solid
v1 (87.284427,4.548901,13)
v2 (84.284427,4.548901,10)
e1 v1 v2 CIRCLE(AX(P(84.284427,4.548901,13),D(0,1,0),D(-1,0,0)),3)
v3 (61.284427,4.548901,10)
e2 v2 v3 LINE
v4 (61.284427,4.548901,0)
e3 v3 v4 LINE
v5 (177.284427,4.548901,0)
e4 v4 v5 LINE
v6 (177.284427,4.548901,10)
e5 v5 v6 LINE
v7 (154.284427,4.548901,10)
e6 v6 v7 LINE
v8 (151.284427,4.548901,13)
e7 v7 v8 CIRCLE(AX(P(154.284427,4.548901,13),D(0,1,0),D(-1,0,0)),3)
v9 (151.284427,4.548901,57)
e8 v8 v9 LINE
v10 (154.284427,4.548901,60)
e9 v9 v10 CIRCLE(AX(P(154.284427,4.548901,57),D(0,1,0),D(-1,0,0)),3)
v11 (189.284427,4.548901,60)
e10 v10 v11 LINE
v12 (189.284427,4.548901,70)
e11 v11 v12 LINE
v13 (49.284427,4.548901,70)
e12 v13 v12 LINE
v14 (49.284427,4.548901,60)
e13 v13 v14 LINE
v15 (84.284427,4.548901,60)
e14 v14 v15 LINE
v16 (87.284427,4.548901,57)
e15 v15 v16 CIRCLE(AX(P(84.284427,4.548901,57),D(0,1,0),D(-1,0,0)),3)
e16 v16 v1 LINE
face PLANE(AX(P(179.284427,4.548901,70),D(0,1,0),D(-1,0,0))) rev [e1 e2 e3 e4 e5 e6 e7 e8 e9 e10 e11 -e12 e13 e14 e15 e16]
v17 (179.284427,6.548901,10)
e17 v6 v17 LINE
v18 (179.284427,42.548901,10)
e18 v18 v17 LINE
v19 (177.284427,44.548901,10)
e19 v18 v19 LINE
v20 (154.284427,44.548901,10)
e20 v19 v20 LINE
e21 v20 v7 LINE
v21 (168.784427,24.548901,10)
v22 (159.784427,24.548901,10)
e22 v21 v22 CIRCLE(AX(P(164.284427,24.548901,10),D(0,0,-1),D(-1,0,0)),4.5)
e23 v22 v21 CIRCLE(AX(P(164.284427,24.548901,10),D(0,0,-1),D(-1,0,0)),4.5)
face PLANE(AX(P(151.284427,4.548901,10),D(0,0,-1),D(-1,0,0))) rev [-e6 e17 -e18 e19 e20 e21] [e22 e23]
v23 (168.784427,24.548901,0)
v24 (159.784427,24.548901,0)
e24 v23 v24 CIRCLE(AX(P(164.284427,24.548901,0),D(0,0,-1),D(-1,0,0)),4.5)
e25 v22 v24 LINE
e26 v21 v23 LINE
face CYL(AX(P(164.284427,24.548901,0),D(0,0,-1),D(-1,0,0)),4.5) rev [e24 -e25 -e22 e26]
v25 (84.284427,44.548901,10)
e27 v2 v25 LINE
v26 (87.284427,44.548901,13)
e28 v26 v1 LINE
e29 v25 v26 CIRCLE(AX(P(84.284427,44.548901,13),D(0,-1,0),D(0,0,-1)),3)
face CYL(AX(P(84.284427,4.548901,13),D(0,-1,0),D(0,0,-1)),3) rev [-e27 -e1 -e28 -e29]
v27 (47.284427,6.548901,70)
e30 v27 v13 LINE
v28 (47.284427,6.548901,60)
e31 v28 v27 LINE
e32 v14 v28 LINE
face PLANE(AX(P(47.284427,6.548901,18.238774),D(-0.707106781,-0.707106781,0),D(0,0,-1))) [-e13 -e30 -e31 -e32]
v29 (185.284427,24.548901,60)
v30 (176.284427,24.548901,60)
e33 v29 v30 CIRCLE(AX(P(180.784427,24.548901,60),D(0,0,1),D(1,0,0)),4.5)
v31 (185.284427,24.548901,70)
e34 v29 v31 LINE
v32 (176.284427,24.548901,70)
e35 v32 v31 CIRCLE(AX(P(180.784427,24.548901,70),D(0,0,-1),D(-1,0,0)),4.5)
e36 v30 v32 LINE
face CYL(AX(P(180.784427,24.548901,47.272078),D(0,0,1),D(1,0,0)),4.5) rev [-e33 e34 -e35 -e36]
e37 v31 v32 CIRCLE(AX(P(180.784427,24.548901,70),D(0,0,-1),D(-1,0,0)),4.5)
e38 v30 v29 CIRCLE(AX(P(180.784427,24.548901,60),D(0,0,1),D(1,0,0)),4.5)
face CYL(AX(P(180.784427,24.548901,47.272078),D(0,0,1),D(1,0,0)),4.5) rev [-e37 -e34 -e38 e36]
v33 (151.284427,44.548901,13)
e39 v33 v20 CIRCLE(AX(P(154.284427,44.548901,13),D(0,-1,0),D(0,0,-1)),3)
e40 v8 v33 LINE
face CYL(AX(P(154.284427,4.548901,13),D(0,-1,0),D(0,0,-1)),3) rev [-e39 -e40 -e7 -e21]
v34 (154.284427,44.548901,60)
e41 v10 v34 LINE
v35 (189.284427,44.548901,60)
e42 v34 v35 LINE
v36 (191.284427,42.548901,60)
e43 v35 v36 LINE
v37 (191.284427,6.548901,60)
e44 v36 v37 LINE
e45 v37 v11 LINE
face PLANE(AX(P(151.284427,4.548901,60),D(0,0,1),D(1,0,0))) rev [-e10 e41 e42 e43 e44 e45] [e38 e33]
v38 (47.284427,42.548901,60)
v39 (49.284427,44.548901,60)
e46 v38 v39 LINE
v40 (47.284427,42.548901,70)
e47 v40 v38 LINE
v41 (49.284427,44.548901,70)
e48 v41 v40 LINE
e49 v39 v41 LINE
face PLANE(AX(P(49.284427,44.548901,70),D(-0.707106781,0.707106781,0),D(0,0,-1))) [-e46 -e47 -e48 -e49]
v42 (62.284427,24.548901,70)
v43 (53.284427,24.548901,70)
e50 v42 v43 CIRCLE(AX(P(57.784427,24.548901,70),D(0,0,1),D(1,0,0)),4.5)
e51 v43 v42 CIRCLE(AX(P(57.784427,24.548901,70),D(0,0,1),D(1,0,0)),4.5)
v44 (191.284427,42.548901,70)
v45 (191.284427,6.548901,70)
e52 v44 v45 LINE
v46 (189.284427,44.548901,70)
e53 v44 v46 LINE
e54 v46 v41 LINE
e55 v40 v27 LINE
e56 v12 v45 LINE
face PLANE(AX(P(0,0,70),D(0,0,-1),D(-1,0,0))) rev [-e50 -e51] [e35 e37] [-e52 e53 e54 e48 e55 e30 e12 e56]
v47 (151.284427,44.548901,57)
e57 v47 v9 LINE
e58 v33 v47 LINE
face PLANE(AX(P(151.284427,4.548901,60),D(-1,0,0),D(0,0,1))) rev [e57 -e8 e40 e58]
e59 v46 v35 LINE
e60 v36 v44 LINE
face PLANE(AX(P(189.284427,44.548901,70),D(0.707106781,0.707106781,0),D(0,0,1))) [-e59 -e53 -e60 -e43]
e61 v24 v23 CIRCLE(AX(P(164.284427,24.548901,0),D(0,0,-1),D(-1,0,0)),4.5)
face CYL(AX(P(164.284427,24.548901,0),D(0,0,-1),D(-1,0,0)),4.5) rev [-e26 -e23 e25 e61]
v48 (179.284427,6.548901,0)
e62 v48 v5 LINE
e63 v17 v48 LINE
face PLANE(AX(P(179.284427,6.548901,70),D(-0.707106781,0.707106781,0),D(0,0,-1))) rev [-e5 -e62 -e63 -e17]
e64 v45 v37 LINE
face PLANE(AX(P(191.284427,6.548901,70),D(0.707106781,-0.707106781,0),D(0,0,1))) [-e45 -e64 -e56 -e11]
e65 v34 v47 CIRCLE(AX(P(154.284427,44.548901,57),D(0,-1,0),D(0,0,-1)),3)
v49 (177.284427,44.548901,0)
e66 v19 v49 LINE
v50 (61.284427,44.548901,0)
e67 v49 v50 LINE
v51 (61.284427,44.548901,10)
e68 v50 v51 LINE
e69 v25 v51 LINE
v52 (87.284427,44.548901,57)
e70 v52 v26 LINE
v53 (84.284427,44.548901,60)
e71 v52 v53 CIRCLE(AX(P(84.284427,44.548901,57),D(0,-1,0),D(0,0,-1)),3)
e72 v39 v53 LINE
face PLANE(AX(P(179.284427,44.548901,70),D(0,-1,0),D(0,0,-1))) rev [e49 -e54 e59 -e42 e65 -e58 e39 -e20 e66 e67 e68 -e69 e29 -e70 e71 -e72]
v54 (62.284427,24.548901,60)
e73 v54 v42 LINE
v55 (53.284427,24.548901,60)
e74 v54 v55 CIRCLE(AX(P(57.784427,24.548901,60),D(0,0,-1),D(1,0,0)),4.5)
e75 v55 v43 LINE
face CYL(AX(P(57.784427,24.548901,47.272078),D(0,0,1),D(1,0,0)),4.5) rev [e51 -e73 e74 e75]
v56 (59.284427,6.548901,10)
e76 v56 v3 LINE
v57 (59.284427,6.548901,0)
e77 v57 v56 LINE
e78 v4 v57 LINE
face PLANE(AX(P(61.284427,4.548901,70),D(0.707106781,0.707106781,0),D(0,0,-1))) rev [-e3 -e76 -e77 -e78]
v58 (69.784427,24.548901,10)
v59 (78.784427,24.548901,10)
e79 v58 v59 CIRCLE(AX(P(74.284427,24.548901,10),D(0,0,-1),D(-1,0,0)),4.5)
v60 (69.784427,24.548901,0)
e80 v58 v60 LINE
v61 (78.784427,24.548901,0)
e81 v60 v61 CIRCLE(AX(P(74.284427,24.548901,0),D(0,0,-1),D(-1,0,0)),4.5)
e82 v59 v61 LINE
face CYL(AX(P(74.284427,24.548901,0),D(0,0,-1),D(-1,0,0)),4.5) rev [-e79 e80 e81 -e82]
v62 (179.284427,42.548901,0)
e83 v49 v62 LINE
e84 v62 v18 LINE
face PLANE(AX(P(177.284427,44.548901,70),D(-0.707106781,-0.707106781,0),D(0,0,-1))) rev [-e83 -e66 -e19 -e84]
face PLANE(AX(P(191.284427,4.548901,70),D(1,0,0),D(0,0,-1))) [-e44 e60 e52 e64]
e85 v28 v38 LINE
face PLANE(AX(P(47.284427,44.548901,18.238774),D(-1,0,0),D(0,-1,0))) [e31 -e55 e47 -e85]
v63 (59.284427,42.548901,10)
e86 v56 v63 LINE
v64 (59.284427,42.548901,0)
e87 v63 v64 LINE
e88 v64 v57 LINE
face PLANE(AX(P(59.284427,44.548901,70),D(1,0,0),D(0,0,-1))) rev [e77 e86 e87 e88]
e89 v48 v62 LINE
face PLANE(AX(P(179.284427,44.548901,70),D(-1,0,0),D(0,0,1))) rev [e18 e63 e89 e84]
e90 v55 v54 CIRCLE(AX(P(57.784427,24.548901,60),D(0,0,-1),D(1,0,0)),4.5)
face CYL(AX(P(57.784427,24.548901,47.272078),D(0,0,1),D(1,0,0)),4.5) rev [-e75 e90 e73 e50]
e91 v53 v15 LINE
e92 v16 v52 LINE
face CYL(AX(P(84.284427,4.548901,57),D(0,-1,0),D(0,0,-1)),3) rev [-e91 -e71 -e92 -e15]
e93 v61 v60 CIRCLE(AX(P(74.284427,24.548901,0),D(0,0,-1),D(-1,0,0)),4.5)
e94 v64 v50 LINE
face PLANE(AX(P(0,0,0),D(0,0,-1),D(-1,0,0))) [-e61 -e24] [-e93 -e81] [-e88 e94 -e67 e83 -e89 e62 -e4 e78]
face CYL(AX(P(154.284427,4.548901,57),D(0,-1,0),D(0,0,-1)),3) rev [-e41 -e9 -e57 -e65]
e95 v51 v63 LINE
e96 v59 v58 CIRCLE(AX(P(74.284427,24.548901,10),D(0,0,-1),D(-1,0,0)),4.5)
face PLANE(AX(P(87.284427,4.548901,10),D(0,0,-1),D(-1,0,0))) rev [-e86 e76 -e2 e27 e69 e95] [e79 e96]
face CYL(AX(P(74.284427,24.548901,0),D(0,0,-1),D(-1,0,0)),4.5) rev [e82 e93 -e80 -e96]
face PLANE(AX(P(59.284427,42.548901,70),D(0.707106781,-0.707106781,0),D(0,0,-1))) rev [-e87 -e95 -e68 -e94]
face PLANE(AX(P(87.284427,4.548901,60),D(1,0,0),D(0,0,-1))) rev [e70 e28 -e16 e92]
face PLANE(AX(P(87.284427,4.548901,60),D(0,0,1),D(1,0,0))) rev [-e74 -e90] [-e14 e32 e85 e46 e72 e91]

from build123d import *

# Parameters (mm, degrees)
SKETCH_1_W             = 120
SKETCH_1_H             = 40
EXTRUDE_1_DEPTH        = 70
SKETCH_2_R             = 3
CUT_EXTRUDE_1_DEPTH    = 198.553816398
SKETCH_3_W             = 47.323469883
SKETCH_3_H             = 50
CUT_EXTRUDE_2_DEPTH    = 197.577989194
FILLET_1_R             = 3
SKETCH_4_W             = 12
SKETCH_4_H             = 40
EXTRUDE_2_DEPTH        = 10
SKETCH_5_W             = 12
SKETCH_5_H             = 40
EXTRUDE_3_DEPTH        = 10
SKETCH_6_R             = 3
EXTRUDE_4_DEPTH        = 10
SKETCH_7_R             = 4.5
CUT_EXTRUDE_3_DEPTH    = 10
CHAMFER_1_SIZE         = 2
HOLE_WIZARD_M8_1_D     = 9
HOLE_WIZARD_M8_1_DEPTH = 19.75
HOLE_WIZARD_M8_1_TIP   = 2.703872786


with BuildPart() as part:
    # 草图1 → 凸台-拉伸1 (new body)
    with BuildSketch(Plane.XY):
        with Locations((119.284427197, 24.548900527)):
            Rectangle(SKETCH_1_W, SKETCH_1_H)
    extrude(amount=EXTRUDE_1_DEPTH)

    # 草图2 → 切除-拉伸1 (cut, through all)
    with BuildSketch(Plane.XY.offset(70)):
        with Locations((74.284427197, 24.548900527)):
            Circle(SKETCH_2_R)
        with Locations((164.284427197, 24.548900527)):
            Circle(SKETCH_2_R)
    extrude(amount=-CUT_EXTRUDE_1_DEPTH, mode=Mode.SUBTRACT)

    # 草图3 → 切除-拉伸2 (cut, through all)
    with BuildSketch(Plane(origin=(0, 44.548900527, 0), x_dir=(1, 0, 0), z_dir=(0, 1, 0))):
        with Locations((174.946162139, -35)):
            Rectangle(SKETCH_3_W, SKETCH_3_H)
        with Locations((63.622692255, -35)):
            Rectangle(SKETCH_3_W, SKETCH_3_H)
    extrude(amount=-CUT_EXTRUDE_2_DEPTH, mode=Mode.SUBTRACT)

    # 圆角1
    fillet_1_edges = [part.edges().sort_by_distance(p)[0] for p in [
        (151.284427197, 24.548900527, 10),
        (151.284427197, 24.548900527, 60),
        (87.284427197, 24.548900527, 60),
        (87.284427197, 24.548900527, 10),
    ]]
    fillet(fillet_1_edges, radius=FILLET_1_R)

    # 草图4 → 凸台-拉伸2 (add)
    with BuildSketch(Plane(origin=(0, 0, 60), x_dir=(-1, 0, 0), z_dir=(0, 0, -1))):
        with Locations((-185.284427197, 24.548900527)):
            Rectangle(SKETCH_4_W, SKETCH_4_H)
    extrude(amount=-EXTRUDE_2_DEPTH)

    # 草图5 → 凸台-拉伸3 (add)
    with BuildSketch(Plane.XY.offset(70)):
        with Locations((53.284427197, 24.548900527)):
            Rectangle(SKETCH_5_W, SKETCH_5_H)
    extrude(amount=-EXTRUDE_3_DEPTH)

    # 草图6 → 凸台-拉伸4 (add)
    with BuildSketch(Plane.XY.offset(70)):
        with Locations((74.284427197, 24.548900527)):
            Circle(SKETCH_6_R)
        with Locations((164.284427197, 24.548900527)):
            Circle(SKETCH_6_R)
    extrude(amount=-EXTRUDE_4_DEPTH)

    # 草图7 → 切除-拉伸3 (cut)
    with BuildSketch(Plane.XY.offset(70)):
        with Locations((57.784427197, 24.548900527)):
            Circle(SKETCH_7_R)
    cut_extrude_3 = extrude(amount=-CUT_EXTRUDE_3_DEPTH, mode=Mode.SUBTRACT)

    # 镜向2: 切除-拉伸3 across plane
    add(cut_extrude_3.mirror(Plane(origin=(119.284427197, 0, 0), x_dir=(0, 0, 1), z_dir=(1, 0, 0))), mode=Mode.SUBTRACT)

    # 倒角1
    chamfer_1_edges = [part.edges().sort_by_distance(p)[0] for p in [
        (47.284427197, 4.548900527, 65),
        (47.284427197, 44.548900527, 65),
        (179.284427197, 4.548900527, 5),
        (179.284427197, 44.548900527, 5),
        (59.284427197, 4.548900527, 5),
        (59.284427197, 44.548900527, 5),
        (191.284427197, 4.548900527, 65),
        (191.284427197, 44.548900527, 65),
    ]]
    chamfer(chamfer_1_edges, length=CHAMFER_1_SIZE)

    # Hole Wizard M8 _1
    with Locations(Plane(origin=(74.284427197, 24.548900527, 0), x_dir=(-1, 0, 0), z_dir=(0, 0, -1))):
        with Locations((0, 0), (-90, 0)):
            Hole(HOLE_WIZARD_M8_1_D / 2, depth=HOLE_WIZARD_M8_1_DEPTH)
            with Locations((0, 0, -(HOLE_WIZARD_M8_1_DEPTH + HOLE_WIZARD_M8_1_TIP / 2))):  # 118° drill point
                Cone(0, HOLE_WIZARD_M8_1_D / 2, HOLE_WIZARD_M8_1_TIP, mode=Mode.SUBTRACT)


solid = part.part
